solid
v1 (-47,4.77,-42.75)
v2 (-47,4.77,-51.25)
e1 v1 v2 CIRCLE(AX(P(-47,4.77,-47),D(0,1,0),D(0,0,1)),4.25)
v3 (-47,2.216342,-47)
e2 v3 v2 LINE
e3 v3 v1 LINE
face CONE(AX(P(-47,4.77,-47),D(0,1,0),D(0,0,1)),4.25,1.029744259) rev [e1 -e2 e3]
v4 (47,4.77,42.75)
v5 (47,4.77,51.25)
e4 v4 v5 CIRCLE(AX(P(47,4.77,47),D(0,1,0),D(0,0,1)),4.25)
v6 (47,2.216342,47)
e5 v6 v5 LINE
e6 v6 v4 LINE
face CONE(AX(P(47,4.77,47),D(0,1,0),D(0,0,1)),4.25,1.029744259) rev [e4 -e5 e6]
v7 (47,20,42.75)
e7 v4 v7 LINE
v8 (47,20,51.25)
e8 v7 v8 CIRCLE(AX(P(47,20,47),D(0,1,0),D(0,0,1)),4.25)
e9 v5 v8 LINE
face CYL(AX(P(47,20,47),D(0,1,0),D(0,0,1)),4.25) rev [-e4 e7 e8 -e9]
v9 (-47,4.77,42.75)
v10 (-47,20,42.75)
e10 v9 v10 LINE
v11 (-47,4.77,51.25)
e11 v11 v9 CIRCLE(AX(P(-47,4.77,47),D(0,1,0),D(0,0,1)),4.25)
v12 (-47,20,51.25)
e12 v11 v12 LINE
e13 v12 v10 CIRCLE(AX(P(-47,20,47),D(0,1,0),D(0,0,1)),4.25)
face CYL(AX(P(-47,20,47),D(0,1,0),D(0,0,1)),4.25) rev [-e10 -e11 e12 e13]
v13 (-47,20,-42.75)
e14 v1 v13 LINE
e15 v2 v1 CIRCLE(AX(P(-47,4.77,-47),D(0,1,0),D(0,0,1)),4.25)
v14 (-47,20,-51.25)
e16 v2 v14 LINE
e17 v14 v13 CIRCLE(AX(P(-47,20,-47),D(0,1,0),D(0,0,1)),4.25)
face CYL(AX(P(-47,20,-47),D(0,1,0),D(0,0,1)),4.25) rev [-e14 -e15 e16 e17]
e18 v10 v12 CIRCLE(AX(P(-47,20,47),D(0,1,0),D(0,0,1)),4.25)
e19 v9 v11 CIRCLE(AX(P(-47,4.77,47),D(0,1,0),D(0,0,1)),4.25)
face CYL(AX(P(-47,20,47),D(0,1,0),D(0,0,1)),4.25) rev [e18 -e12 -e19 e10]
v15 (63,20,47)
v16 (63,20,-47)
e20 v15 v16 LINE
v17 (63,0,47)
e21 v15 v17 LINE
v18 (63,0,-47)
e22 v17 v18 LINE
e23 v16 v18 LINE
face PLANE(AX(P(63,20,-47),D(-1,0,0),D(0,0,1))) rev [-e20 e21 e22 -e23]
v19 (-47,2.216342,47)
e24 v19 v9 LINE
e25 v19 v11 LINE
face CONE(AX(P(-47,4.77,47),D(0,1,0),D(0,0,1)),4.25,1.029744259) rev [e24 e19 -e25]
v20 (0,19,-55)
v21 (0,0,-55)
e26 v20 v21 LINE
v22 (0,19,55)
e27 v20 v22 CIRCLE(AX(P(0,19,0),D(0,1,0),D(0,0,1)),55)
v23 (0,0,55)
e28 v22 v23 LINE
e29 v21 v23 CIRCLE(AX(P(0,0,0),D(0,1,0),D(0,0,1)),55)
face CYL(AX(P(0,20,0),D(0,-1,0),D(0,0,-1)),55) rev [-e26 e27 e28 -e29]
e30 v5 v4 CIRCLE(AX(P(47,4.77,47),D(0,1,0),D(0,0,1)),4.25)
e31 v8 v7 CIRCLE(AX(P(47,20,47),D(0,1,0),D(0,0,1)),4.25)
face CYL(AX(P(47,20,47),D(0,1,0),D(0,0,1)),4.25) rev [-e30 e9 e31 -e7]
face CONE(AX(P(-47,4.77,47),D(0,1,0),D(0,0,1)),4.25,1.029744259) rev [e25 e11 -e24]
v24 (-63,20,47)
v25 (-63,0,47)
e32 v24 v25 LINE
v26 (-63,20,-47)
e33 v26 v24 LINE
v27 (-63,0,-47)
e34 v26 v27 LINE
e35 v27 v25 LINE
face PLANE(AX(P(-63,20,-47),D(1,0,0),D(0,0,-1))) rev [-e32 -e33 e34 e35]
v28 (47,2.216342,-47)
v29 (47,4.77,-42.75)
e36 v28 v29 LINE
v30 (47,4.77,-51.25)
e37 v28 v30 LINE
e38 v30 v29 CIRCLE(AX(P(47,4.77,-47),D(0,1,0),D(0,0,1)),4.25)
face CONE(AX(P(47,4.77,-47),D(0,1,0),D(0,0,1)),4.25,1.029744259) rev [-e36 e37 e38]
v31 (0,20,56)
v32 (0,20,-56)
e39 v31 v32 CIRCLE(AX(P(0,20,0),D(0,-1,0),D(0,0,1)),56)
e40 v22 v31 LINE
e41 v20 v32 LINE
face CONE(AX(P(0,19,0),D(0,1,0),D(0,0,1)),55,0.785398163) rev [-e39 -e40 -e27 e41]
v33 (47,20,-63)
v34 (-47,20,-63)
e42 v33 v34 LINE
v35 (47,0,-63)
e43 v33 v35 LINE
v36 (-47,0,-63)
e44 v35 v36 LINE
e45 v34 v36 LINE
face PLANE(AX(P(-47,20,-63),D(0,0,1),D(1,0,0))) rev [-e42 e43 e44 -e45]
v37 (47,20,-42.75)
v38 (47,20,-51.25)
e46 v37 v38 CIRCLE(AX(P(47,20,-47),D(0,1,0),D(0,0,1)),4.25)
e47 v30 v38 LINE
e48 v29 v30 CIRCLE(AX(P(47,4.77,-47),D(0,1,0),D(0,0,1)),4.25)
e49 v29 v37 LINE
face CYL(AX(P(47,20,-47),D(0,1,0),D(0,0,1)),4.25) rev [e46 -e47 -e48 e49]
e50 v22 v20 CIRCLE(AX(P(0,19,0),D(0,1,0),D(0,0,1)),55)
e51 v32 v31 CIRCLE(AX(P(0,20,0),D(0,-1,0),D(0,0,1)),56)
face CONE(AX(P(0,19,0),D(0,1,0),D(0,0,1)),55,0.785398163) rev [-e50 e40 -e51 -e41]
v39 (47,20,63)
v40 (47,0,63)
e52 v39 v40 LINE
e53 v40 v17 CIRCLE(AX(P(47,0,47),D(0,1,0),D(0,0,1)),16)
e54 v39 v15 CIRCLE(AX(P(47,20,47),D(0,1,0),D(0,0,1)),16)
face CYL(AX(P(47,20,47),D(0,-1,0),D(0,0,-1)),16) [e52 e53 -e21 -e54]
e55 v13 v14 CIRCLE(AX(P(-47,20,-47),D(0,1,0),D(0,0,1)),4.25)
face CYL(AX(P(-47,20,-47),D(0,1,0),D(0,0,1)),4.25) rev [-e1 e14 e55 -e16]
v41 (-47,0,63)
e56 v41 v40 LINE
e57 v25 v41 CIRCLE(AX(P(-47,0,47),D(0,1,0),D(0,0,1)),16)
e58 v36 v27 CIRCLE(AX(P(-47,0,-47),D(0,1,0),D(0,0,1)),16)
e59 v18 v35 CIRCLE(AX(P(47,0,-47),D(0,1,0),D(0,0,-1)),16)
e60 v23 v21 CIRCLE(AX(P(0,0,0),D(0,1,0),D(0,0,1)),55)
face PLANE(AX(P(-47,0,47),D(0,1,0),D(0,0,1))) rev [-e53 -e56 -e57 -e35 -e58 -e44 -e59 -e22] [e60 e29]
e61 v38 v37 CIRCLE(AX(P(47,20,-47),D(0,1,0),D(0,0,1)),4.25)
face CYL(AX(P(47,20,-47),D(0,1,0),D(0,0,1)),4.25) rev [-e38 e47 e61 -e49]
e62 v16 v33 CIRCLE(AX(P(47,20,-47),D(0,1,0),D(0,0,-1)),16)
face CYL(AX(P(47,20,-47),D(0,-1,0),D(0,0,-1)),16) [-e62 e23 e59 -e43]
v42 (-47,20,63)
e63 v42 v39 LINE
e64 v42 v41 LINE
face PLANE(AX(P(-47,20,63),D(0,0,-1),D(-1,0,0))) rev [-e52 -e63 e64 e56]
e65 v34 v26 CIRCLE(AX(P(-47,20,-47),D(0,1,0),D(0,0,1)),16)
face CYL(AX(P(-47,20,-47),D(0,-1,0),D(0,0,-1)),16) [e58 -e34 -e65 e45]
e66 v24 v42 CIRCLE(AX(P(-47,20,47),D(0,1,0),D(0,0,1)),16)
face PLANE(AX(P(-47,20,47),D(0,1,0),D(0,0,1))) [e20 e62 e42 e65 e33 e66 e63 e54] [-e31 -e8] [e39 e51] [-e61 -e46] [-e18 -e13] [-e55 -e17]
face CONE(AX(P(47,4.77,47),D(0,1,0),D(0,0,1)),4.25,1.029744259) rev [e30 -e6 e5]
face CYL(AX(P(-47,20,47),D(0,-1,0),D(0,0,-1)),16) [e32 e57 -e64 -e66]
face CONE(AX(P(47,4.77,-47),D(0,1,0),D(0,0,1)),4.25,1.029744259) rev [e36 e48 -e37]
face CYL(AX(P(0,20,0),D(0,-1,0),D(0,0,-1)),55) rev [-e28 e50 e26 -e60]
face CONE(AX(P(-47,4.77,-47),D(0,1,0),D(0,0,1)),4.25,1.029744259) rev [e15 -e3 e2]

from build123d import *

# Parameters (mm, degrees)
SKETCH1_R              = 55
BOSS_EXTRUDE1_DEPTH    = 20
SKETCH2_R              = 4
CUT_EXTRUDE1_DEPTH     = 3
M10_TAPPED_HOLE1_D     = 8.5
M10_TAPPED_HOLE1_DEPTH = 15.23
M10_TAPPED_HOLE1_TIP   = 2.553657631
CHAMFER1_SIZE          = 1


with BuildPart() as part:
    # Sketch1 → Boss-Extrude1 (new body)
    with BuildSketch(Plane(origin=(0, 0, 0), x_dir=(1, 0, 0), z_dir=(0, 1, 0))):
        with BuildLine():
            Line((-47, 63), (47, 63))
            ThreePointArc((47, 63), (58.313708499, 58.313708499), (63, 47))
            Line((63, 47), (63, -47))
            ThreePointArc((63, -47), (58.313708499, -58.313708499), (47, -63))
            Line((47, -63), (-47, -63))
            ThreePointArc((-47, -63), (-58.313708499, -58.313708499), (-63, -47))
            Line((-63, -47), (-63, 47))
            ThreePointArc((-63, 47), (-58.313708499, 58.313708499), (-47, 63))
        make_face()
        with Locations(Location((0, 0, 0), (0, 0, 270))):
            Circle(SKETCH1_R, mode=Mode.SUBTRACT)
    extrude(amount=BOSS_EXTRUDE1_DEPTH)

    # Sketch2 → Cut-Extrude1 (cut)
    with BuildSketch(Plane(origin=(0, 20, 0), x_dir=(1, 0, 0), z_dir=(0, 1, 0))):
        with Locations(Location((-47, 47, 0), (0, 0, 270))):
            Circle(SKETCH2_R)
        with Locations(Location((47, 47, 0), (0, 0, 270))):
            Circle(SKETCH2_R)
        with Locations(Location((47, -47, 0), (0, 0, 270))):
            Circle(SKETCH2_R)
        with Locations(Location((-47, -47, 0), (0, 0, 270))):
            Circle(SKETCH2_R)
    extrude(amount=-CUT_EXTRUDE1_DEPTH, mode=Mode.SUBTRACT)

    # M10 Tapped Hole1
    with Locations(Plane(origin=(0, 20, 0), x_dir=(1, 0, 0), z_dir=(0, 1, 0))):
        with Locations((-47, 47), (47, 47), (47, -47), (-47, -47)):
            Hole(M10_TAPPED_HOLE1_D / 2, depth=M10_TAPPED_HOLE1_DEPTH)
            with Locations((0, 0, -(M10_TAPPED_HOLE1_DEPTH + M10_TAPPED_HOLE1_TIP / 2))):  # 118° drill point
                Cone(0, M10_TAPPED_HOLE1_D / 2, M10_TAPPED_HOLE1_TIP, mode=Mode.SUBTRACT)

    # Chamfer1
    chamfer1_edges = [part.edges().sort_by_distance(p)[0] for p in [
        (0, 20, -55),
    ]]
    chamfer(chamfer1_edges, length=CHAMFER1_SIZE)


solid = part.part
